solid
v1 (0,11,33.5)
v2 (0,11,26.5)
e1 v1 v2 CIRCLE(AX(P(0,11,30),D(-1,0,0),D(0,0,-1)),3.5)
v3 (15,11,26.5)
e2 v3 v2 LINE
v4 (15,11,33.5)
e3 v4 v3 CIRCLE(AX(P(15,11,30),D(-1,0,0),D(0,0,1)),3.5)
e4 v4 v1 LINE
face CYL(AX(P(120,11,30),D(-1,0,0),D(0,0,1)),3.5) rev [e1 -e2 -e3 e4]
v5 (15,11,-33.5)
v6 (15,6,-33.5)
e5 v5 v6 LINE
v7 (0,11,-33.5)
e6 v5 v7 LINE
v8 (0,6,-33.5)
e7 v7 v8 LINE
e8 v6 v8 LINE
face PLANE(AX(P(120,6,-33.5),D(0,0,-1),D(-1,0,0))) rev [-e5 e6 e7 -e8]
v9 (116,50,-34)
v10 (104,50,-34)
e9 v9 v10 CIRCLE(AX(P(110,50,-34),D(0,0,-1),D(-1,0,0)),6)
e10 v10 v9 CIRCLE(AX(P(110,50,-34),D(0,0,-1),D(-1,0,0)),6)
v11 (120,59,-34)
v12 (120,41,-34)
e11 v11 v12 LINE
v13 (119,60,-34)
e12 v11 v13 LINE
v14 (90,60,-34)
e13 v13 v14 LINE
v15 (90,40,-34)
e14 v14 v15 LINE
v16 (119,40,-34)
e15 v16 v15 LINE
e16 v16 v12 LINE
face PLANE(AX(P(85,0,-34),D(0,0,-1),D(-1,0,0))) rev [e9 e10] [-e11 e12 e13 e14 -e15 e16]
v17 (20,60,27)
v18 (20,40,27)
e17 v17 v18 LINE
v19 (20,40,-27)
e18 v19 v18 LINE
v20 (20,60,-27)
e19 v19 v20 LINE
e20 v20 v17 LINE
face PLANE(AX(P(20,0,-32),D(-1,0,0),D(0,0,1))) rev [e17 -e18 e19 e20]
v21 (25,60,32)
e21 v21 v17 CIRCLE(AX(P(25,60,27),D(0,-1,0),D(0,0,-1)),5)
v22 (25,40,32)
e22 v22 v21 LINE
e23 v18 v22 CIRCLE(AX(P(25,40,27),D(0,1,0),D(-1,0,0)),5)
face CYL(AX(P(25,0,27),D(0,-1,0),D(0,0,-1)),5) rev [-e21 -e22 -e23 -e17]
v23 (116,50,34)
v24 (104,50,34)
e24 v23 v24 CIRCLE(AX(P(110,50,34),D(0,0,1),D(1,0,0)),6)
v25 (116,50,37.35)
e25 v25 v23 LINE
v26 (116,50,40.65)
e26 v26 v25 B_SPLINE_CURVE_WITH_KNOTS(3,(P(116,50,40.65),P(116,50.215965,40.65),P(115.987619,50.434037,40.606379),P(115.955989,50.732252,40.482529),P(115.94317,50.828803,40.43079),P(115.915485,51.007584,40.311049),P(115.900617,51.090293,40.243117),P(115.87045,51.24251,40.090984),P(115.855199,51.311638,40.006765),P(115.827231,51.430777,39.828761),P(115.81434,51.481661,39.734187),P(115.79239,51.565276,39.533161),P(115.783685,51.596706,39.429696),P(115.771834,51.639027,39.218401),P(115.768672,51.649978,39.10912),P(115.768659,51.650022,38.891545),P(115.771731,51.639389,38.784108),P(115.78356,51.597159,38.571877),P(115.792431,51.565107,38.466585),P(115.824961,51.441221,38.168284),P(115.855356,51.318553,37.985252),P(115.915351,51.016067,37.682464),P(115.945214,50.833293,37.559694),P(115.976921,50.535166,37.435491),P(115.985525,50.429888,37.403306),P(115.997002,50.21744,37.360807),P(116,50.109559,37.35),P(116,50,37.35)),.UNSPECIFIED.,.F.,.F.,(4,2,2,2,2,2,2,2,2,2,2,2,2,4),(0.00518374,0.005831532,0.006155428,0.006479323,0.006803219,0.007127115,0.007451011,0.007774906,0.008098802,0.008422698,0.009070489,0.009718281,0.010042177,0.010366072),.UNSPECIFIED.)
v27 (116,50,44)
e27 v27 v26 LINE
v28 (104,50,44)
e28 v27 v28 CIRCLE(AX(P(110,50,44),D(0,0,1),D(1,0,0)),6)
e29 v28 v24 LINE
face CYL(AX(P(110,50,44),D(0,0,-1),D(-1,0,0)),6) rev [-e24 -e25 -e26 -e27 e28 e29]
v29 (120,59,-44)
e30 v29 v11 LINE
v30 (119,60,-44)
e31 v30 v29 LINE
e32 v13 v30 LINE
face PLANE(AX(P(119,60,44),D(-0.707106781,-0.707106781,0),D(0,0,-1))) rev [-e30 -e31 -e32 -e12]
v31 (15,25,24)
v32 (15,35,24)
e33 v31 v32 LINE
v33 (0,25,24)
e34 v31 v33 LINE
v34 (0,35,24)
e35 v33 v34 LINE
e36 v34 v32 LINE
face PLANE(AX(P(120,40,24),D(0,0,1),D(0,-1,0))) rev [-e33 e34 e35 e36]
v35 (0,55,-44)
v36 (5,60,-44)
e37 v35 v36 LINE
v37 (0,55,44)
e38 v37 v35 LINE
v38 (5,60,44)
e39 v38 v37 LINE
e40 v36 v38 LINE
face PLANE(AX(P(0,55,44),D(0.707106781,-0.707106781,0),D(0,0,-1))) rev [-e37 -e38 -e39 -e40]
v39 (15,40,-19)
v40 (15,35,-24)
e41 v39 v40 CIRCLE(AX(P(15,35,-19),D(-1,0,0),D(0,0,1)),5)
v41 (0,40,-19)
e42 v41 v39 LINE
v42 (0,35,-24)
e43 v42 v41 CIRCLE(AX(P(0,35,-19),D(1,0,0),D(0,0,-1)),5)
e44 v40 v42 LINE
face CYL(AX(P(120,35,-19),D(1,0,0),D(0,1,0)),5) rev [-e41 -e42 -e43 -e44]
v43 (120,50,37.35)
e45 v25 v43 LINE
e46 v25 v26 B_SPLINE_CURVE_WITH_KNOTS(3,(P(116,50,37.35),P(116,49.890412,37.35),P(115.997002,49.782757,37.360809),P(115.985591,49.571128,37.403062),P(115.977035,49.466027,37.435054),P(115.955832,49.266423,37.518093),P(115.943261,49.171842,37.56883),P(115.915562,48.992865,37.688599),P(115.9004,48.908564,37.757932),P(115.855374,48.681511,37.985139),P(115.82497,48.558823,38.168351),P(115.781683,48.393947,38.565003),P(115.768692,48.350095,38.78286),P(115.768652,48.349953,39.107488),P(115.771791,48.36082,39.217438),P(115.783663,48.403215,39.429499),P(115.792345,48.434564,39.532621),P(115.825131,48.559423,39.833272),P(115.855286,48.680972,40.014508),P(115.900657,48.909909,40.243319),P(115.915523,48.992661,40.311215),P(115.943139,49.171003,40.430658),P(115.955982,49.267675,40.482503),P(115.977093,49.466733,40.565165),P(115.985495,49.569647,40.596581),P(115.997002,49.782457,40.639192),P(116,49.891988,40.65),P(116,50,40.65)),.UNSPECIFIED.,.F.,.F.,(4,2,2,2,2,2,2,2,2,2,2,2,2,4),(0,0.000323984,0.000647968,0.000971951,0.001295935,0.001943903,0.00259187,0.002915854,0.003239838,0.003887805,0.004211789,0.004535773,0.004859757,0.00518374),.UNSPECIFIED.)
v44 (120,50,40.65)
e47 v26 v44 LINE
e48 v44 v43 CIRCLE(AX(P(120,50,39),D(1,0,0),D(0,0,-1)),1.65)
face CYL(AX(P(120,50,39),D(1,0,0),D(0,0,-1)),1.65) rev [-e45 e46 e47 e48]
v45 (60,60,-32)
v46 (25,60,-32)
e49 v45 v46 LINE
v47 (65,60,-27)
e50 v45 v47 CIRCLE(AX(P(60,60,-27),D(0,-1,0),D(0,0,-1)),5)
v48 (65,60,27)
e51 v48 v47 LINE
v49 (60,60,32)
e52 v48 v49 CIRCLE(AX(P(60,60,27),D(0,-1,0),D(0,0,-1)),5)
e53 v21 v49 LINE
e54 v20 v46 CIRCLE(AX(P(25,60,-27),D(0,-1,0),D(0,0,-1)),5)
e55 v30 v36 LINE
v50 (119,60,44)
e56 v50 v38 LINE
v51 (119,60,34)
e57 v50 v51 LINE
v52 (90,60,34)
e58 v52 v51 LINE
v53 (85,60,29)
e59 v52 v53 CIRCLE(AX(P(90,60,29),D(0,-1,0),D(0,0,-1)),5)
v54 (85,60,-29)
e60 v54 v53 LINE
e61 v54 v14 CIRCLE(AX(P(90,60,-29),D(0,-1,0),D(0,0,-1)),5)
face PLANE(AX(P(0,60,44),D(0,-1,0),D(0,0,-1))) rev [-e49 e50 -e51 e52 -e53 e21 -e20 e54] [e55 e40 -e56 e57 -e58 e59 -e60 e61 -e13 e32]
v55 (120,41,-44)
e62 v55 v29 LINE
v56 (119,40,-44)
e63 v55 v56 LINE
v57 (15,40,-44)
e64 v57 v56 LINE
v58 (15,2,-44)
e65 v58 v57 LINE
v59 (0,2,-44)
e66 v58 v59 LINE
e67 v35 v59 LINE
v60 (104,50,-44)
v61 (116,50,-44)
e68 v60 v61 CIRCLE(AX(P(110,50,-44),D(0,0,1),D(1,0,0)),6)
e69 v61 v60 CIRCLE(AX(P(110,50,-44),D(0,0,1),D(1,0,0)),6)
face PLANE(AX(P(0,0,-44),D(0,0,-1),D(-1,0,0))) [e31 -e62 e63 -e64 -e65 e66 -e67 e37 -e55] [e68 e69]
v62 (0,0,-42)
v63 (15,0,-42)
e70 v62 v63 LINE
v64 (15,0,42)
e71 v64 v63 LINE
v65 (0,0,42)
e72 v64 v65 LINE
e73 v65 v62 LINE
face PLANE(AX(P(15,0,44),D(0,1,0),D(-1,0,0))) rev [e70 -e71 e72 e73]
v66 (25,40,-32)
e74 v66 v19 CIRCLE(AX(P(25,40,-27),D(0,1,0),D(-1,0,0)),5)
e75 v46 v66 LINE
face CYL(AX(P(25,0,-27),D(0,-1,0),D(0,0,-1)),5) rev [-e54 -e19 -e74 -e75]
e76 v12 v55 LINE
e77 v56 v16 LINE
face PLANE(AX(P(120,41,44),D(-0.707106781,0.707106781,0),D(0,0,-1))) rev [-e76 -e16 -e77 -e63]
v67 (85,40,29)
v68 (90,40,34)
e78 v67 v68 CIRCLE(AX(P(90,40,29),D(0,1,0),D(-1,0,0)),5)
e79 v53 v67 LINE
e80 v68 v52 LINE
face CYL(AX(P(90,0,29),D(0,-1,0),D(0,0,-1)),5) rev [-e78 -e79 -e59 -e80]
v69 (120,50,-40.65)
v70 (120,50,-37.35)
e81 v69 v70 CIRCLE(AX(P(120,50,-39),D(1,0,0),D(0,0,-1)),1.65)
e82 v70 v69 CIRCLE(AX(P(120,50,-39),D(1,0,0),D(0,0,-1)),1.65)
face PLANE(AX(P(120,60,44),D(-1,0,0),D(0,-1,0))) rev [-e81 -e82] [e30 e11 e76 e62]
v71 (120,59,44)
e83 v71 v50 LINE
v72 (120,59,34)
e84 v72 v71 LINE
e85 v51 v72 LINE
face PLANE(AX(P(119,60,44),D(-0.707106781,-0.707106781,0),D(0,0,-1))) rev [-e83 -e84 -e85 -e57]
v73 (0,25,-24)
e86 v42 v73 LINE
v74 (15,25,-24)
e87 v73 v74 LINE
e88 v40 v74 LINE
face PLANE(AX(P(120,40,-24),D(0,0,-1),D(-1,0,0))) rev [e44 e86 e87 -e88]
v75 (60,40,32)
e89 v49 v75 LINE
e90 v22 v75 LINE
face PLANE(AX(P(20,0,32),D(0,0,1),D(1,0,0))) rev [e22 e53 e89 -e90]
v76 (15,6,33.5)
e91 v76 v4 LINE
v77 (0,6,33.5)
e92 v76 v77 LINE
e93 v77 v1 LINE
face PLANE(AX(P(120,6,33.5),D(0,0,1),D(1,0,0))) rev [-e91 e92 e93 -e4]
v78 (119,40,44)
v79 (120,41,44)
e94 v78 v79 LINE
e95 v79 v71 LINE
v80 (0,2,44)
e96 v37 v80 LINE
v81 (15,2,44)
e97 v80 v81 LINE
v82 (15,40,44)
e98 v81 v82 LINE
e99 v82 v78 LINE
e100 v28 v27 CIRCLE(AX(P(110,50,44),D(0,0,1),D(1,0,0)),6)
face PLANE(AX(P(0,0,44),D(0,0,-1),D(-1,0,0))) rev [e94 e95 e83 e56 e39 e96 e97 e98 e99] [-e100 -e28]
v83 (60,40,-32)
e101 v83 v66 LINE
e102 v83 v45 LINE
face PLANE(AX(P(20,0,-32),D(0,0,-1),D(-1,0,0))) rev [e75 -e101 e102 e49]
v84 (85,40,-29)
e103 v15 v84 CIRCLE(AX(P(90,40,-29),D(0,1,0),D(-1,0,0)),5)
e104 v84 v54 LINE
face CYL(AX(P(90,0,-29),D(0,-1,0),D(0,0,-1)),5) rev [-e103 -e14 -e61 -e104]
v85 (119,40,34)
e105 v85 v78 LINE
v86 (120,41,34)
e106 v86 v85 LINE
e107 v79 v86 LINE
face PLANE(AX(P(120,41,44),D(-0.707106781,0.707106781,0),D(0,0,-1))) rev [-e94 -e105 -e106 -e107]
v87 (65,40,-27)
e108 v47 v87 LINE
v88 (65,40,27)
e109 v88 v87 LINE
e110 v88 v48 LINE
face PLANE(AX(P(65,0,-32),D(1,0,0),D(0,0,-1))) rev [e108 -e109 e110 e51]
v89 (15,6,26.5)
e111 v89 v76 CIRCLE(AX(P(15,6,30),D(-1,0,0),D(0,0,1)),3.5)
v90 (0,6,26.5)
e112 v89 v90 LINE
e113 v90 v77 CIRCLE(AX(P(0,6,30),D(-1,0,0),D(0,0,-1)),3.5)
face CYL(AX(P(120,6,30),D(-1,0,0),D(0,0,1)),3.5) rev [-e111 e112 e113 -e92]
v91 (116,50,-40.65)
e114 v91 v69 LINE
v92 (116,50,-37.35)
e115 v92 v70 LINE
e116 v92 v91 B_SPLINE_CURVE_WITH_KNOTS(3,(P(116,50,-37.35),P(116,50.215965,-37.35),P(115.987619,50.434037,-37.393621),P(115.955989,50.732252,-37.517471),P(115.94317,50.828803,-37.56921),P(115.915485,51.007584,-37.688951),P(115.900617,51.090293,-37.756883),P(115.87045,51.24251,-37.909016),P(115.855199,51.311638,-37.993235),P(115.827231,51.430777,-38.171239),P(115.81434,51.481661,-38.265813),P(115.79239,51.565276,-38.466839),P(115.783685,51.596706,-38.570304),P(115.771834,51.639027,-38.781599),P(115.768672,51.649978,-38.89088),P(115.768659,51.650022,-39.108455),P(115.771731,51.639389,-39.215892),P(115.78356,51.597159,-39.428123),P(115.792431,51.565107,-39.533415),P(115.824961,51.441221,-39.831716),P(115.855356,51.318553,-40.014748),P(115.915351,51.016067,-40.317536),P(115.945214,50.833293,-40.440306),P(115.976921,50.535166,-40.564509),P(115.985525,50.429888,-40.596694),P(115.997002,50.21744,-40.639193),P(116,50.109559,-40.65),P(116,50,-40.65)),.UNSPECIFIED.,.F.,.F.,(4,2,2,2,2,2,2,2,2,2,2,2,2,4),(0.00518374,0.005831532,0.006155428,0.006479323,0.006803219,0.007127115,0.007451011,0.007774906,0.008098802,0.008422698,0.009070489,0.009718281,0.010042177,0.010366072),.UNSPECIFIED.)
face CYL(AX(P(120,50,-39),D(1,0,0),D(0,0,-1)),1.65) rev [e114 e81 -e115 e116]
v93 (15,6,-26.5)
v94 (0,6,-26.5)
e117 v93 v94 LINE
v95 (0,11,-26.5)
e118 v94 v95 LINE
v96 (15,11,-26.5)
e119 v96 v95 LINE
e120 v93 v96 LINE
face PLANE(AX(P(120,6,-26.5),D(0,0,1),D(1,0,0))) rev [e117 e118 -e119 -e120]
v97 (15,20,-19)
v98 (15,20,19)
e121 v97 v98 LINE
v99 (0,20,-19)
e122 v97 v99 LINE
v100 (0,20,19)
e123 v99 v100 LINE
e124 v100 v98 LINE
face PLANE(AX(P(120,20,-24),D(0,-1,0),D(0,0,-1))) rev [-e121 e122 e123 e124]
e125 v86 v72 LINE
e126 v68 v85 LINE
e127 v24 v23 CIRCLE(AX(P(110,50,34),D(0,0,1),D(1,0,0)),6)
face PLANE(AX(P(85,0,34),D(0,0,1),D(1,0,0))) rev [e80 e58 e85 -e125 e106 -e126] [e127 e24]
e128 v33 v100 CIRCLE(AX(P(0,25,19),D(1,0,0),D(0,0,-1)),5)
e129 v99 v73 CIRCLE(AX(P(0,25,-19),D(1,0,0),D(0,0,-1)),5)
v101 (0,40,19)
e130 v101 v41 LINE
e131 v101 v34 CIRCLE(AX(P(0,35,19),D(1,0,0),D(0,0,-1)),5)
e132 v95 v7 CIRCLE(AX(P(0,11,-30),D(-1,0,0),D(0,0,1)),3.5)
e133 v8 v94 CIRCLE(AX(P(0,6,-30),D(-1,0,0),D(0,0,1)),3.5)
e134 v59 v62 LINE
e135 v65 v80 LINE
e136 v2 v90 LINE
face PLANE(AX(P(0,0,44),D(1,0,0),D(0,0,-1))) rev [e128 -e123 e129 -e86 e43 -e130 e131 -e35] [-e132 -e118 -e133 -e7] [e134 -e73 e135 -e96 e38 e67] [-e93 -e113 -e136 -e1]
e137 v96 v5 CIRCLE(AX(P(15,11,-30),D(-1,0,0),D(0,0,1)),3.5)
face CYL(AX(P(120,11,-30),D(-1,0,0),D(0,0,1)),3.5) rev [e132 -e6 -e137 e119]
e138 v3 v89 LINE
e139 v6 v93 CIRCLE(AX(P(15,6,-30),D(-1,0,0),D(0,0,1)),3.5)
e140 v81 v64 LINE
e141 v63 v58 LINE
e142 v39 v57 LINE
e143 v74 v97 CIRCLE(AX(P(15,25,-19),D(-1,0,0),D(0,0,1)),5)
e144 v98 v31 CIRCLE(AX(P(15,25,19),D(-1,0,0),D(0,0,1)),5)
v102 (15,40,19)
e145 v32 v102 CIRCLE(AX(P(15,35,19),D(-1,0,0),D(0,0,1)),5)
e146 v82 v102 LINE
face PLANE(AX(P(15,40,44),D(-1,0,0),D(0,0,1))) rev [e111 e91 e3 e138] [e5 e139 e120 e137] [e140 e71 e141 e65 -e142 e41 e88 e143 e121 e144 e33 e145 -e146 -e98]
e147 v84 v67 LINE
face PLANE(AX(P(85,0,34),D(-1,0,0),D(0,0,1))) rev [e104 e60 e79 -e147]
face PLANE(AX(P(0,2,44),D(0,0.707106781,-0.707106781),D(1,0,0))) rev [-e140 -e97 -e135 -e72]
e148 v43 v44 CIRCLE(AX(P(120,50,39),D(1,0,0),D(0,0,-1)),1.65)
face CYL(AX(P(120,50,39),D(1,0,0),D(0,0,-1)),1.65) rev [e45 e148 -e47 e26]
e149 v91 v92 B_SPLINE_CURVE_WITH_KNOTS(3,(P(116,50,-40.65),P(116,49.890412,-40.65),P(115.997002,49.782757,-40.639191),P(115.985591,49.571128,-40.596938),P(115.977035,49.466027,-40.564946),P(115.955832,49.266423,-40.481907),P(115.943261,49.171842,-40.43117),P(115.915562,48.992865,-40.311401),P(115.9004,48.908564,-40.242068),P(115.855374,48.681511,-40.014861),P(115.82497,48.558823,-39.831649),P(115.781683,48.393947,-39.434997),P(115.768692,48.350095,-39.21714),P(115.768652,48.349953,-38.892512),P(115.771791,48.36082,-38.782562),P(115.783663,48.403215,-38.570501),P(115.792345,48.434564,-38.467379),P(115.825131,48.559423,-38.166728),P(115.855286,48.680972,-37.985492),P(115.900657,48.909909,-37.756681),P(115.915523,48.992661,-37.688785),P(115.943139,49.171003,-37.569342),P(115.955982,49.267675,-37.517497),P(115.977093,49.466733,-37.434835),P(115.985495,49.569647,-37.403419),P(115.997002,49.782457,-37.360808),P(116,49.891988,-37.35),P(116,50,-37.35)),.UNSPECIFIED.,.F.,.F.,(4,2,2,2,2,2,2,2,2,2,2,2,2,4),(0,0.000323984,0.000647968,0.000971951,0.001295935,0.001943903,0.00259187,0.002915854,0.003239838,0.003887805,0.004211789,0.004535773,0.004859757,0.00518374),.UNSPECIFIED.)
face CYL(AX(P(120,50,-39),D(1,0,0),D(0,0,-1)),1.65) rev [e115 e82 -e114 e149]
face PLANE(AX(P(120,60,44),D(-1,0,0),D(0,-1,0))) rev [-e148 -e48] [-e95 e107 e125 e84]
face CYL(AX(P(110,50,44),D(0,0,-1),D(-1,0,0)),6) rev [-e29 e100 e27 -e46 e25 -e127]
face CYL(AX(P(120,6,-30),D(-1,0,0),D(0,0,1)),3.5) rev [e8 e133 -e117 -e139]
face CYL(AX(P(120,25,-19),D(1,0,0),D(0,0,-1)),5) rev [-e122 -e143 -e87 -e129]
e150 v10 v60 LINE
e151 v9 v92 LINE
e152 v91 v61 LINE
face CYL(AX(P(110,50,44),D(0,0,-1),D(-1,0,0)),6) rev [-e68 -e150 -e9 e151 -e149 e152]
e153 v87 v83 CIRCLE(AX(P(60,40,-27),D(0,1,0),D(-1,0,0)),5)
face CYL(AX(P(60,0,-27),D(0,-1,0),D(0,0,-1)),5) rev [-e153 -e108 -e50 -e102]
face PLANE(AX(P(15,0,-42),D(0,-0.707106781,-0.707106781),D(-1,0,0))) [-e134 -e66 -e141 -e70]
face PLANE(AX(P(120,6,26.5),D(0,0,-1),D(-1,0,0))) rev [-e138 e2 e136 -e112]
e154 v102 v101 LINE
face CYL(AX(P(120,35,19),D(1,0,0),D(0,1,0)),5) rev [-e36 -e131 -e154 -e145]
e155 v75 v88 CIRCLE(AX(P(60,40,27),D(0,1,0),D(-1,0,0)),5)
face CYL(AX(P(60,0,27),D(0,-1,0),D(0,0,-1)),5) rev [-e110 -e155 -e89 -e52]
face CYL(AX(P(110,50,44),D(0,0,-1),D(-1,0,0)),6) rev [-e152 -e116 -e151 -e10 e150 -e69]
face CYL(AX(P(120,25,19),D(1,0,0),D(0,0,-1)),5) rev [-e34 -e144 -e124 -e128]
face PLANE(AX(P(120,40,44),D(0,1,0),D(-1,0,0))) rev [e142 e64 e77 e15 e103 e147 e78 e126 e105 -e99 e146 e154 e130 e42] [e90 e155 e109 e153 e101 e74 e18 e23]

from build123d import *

# Parameters (mm, degrees)
SKETCH1_R             = 6
BOSS_EXTRUDE1_DEPTH   = 44
SKETCH2_W             = 70
SKETCH2_H             = 68
CUT_EXTRUDE1_DEPTH    = 142.194900758
CUT_EXTRUDE2_DEPTH    = 142.194900758
M4_TAPPED_HOLE1_D     = 3.3
M4_TAPPED_HOLE1_DEPTH = 10.1
M4_TAPPED_HOLE1_TIP   = 0.991420021
SKETCH7_W             = 45
SKETCH7_H             = 64
CUT_EXTRUDE4_DEPTH    = 142.194900874
SKETCH8_W             = 48
SKETCH8_H             = 20
CUT_EXTRUDE5_DEPTH    = 142.194900874
CHAMFER1_SIZE         = 5
CHAMFER2_SIZE         = 2
CHAMFER3_SIZE         = 1
FILLET1_R             = 5


with BuildPart() as part:
    # Sketch1 → Boss-Extrude1 (new, symmetric)
    with BuildSketch(Plane.XY):
        Polygon((0, 0), (0, 60), (120, 60), (120, 40), (15, 40), (15, 0), align=None)
        with Locations((110, 50)):
            Circle(SKETCH1_R, mode=Mode.SUBTRACT)
    extrude(amount=BOSS_EXTRUDE1_DEPTH, both=True)

    # Sketch2 → Cut-Extrude1 (cut, through all)
    with BuildSketch(Plane(origin=(0, 60, 0), x_dir=(1, 0, 0), z_dir=(0, 1, 0))):
        with Locations((120, 0)):
            Rectangle(SKETCH2_W, SKETCH2_H)
    extrude(amount=-CUT_EXTRUDE1_DEPTH, mode=Mode.SUBTRACT)

    # Sketch3 → Cut-Extrude2 (cut, through all)
    with BuildSketch(Plane.ZY):
        with BuildLine():
            Line((-33.5, 6), (-33.5, 11))
            ThreePointArc((-33.5, 11), (-30, 14.5), (-26.5, 11))
            Line((-26.5, 11), (-26.5, 6))
            ThreePointArc((-26.5, 6), (-30, 2.5), (-33.5, 6))
        make_face()
        with BuildLine():
            Line((33.5, 6), (33.5, 11))
            ThreePointArc((33.5, 11), (30, 14.5), (26.5, 11))
            Line((26.5, 11), (26.5, 6))
            ThreePointArc((26.5, 6), (30, 2.5), (33.5, 6))
        make_face()
    extrude(amount=-CUT_EXTRUDE2_DEPTH, mode=Mode.SUBTRACT)

    # M4 Tapped Hole1
    with Locations(Plane(origin=(120, 0, 0), x_dir=(0, 0, -1), z_dir=(1, 0, 0))):
        with Locations((-39, 50), (39, 50)):
            Hole(M4_TAPPED_HOLE1_D / 2, depth=M4_TAPPED_HOLE1_DEPTH)
            with Locations((0, 0, -(M4_TAPPED_HOLE1_DEPTH + M4_TAPPED_HOLE1_TIP / 2))):  # 118° drill point
                Cone(0, M4_TAPPED_HOLE1_D / 2, M4_TAPPED_HOLE1_TIP, mode=Mode.SUBTRACT)

    # Sketch7 → Cut-Extrude4 (cut, through all)
    with BuildSketch(Plane(origin=(0, 60, 0), x_dir=(-1, 0, 0), z_dir=(0, 1, 0))):
        with Locations((-42.5, 0)):
            Rectangle(SKETCH7_W, SKETCH7_H)
    extrude(amount=-CUT_EXTRUDE4_DEPTH, mode=Mode.SUBTRACT)

    # Sketch8 → Cut-Extrude5 (cut, through all)
    with BuildSketch(Plane.ZY):
        with Locations((0, 30)):
            Rectangle(SKETCH8_W, SKETCH8_H)
    extrude(amount=-CUT_EXTRUDE5_DEPTH, mode=Mode.SUBTRACT)

    # Chamfer1
    chamfer1_edges = [part.edges().sort_by_distance(p)[0] for p in [
        (0, 60, 0),
    ]]
    chamfer(chamfer1_edges, length=CHAMFER1_SIZE)

    # Chamfer2
    chamfer2_edges = [part.edges().sort_by_distance(p)[0] for p in [
        (7.5, 0, 44),
        (7.5, 0, -44),
    ]]
    chamfer(chamfer2_edges, length=CHAMFER2_SIZE)

    # Chamfer3
    chamfer3_edges = [part.edges().sort_by_distance(p)[0] for p in [
        (120, 60, 39),
        (120, 40, 39),
        (120, 60, -39),
        (120, 40, -39),
    ]]
    chamfer(chamfer3_edges, length=CHAMFER3_SIZE)

    # Fillet1
    fillet1_edges = [part.edges().sort_by_distance(p)[0] for p in [
        (7.5, 40, 24),
        (7.5, 20, 24),
        (7.5, 20, -24),
        (7.5, 40, -24),
        (85, 50, 34),
        (85, 50, -34),
        (65, 50, -32),
        (65, 50, 32),
        (20, 50, 32),
        (20, 50, -32),
    ]]
    fillet(fillet1_edges, radius=FILLET1_R)


solid = part.part
